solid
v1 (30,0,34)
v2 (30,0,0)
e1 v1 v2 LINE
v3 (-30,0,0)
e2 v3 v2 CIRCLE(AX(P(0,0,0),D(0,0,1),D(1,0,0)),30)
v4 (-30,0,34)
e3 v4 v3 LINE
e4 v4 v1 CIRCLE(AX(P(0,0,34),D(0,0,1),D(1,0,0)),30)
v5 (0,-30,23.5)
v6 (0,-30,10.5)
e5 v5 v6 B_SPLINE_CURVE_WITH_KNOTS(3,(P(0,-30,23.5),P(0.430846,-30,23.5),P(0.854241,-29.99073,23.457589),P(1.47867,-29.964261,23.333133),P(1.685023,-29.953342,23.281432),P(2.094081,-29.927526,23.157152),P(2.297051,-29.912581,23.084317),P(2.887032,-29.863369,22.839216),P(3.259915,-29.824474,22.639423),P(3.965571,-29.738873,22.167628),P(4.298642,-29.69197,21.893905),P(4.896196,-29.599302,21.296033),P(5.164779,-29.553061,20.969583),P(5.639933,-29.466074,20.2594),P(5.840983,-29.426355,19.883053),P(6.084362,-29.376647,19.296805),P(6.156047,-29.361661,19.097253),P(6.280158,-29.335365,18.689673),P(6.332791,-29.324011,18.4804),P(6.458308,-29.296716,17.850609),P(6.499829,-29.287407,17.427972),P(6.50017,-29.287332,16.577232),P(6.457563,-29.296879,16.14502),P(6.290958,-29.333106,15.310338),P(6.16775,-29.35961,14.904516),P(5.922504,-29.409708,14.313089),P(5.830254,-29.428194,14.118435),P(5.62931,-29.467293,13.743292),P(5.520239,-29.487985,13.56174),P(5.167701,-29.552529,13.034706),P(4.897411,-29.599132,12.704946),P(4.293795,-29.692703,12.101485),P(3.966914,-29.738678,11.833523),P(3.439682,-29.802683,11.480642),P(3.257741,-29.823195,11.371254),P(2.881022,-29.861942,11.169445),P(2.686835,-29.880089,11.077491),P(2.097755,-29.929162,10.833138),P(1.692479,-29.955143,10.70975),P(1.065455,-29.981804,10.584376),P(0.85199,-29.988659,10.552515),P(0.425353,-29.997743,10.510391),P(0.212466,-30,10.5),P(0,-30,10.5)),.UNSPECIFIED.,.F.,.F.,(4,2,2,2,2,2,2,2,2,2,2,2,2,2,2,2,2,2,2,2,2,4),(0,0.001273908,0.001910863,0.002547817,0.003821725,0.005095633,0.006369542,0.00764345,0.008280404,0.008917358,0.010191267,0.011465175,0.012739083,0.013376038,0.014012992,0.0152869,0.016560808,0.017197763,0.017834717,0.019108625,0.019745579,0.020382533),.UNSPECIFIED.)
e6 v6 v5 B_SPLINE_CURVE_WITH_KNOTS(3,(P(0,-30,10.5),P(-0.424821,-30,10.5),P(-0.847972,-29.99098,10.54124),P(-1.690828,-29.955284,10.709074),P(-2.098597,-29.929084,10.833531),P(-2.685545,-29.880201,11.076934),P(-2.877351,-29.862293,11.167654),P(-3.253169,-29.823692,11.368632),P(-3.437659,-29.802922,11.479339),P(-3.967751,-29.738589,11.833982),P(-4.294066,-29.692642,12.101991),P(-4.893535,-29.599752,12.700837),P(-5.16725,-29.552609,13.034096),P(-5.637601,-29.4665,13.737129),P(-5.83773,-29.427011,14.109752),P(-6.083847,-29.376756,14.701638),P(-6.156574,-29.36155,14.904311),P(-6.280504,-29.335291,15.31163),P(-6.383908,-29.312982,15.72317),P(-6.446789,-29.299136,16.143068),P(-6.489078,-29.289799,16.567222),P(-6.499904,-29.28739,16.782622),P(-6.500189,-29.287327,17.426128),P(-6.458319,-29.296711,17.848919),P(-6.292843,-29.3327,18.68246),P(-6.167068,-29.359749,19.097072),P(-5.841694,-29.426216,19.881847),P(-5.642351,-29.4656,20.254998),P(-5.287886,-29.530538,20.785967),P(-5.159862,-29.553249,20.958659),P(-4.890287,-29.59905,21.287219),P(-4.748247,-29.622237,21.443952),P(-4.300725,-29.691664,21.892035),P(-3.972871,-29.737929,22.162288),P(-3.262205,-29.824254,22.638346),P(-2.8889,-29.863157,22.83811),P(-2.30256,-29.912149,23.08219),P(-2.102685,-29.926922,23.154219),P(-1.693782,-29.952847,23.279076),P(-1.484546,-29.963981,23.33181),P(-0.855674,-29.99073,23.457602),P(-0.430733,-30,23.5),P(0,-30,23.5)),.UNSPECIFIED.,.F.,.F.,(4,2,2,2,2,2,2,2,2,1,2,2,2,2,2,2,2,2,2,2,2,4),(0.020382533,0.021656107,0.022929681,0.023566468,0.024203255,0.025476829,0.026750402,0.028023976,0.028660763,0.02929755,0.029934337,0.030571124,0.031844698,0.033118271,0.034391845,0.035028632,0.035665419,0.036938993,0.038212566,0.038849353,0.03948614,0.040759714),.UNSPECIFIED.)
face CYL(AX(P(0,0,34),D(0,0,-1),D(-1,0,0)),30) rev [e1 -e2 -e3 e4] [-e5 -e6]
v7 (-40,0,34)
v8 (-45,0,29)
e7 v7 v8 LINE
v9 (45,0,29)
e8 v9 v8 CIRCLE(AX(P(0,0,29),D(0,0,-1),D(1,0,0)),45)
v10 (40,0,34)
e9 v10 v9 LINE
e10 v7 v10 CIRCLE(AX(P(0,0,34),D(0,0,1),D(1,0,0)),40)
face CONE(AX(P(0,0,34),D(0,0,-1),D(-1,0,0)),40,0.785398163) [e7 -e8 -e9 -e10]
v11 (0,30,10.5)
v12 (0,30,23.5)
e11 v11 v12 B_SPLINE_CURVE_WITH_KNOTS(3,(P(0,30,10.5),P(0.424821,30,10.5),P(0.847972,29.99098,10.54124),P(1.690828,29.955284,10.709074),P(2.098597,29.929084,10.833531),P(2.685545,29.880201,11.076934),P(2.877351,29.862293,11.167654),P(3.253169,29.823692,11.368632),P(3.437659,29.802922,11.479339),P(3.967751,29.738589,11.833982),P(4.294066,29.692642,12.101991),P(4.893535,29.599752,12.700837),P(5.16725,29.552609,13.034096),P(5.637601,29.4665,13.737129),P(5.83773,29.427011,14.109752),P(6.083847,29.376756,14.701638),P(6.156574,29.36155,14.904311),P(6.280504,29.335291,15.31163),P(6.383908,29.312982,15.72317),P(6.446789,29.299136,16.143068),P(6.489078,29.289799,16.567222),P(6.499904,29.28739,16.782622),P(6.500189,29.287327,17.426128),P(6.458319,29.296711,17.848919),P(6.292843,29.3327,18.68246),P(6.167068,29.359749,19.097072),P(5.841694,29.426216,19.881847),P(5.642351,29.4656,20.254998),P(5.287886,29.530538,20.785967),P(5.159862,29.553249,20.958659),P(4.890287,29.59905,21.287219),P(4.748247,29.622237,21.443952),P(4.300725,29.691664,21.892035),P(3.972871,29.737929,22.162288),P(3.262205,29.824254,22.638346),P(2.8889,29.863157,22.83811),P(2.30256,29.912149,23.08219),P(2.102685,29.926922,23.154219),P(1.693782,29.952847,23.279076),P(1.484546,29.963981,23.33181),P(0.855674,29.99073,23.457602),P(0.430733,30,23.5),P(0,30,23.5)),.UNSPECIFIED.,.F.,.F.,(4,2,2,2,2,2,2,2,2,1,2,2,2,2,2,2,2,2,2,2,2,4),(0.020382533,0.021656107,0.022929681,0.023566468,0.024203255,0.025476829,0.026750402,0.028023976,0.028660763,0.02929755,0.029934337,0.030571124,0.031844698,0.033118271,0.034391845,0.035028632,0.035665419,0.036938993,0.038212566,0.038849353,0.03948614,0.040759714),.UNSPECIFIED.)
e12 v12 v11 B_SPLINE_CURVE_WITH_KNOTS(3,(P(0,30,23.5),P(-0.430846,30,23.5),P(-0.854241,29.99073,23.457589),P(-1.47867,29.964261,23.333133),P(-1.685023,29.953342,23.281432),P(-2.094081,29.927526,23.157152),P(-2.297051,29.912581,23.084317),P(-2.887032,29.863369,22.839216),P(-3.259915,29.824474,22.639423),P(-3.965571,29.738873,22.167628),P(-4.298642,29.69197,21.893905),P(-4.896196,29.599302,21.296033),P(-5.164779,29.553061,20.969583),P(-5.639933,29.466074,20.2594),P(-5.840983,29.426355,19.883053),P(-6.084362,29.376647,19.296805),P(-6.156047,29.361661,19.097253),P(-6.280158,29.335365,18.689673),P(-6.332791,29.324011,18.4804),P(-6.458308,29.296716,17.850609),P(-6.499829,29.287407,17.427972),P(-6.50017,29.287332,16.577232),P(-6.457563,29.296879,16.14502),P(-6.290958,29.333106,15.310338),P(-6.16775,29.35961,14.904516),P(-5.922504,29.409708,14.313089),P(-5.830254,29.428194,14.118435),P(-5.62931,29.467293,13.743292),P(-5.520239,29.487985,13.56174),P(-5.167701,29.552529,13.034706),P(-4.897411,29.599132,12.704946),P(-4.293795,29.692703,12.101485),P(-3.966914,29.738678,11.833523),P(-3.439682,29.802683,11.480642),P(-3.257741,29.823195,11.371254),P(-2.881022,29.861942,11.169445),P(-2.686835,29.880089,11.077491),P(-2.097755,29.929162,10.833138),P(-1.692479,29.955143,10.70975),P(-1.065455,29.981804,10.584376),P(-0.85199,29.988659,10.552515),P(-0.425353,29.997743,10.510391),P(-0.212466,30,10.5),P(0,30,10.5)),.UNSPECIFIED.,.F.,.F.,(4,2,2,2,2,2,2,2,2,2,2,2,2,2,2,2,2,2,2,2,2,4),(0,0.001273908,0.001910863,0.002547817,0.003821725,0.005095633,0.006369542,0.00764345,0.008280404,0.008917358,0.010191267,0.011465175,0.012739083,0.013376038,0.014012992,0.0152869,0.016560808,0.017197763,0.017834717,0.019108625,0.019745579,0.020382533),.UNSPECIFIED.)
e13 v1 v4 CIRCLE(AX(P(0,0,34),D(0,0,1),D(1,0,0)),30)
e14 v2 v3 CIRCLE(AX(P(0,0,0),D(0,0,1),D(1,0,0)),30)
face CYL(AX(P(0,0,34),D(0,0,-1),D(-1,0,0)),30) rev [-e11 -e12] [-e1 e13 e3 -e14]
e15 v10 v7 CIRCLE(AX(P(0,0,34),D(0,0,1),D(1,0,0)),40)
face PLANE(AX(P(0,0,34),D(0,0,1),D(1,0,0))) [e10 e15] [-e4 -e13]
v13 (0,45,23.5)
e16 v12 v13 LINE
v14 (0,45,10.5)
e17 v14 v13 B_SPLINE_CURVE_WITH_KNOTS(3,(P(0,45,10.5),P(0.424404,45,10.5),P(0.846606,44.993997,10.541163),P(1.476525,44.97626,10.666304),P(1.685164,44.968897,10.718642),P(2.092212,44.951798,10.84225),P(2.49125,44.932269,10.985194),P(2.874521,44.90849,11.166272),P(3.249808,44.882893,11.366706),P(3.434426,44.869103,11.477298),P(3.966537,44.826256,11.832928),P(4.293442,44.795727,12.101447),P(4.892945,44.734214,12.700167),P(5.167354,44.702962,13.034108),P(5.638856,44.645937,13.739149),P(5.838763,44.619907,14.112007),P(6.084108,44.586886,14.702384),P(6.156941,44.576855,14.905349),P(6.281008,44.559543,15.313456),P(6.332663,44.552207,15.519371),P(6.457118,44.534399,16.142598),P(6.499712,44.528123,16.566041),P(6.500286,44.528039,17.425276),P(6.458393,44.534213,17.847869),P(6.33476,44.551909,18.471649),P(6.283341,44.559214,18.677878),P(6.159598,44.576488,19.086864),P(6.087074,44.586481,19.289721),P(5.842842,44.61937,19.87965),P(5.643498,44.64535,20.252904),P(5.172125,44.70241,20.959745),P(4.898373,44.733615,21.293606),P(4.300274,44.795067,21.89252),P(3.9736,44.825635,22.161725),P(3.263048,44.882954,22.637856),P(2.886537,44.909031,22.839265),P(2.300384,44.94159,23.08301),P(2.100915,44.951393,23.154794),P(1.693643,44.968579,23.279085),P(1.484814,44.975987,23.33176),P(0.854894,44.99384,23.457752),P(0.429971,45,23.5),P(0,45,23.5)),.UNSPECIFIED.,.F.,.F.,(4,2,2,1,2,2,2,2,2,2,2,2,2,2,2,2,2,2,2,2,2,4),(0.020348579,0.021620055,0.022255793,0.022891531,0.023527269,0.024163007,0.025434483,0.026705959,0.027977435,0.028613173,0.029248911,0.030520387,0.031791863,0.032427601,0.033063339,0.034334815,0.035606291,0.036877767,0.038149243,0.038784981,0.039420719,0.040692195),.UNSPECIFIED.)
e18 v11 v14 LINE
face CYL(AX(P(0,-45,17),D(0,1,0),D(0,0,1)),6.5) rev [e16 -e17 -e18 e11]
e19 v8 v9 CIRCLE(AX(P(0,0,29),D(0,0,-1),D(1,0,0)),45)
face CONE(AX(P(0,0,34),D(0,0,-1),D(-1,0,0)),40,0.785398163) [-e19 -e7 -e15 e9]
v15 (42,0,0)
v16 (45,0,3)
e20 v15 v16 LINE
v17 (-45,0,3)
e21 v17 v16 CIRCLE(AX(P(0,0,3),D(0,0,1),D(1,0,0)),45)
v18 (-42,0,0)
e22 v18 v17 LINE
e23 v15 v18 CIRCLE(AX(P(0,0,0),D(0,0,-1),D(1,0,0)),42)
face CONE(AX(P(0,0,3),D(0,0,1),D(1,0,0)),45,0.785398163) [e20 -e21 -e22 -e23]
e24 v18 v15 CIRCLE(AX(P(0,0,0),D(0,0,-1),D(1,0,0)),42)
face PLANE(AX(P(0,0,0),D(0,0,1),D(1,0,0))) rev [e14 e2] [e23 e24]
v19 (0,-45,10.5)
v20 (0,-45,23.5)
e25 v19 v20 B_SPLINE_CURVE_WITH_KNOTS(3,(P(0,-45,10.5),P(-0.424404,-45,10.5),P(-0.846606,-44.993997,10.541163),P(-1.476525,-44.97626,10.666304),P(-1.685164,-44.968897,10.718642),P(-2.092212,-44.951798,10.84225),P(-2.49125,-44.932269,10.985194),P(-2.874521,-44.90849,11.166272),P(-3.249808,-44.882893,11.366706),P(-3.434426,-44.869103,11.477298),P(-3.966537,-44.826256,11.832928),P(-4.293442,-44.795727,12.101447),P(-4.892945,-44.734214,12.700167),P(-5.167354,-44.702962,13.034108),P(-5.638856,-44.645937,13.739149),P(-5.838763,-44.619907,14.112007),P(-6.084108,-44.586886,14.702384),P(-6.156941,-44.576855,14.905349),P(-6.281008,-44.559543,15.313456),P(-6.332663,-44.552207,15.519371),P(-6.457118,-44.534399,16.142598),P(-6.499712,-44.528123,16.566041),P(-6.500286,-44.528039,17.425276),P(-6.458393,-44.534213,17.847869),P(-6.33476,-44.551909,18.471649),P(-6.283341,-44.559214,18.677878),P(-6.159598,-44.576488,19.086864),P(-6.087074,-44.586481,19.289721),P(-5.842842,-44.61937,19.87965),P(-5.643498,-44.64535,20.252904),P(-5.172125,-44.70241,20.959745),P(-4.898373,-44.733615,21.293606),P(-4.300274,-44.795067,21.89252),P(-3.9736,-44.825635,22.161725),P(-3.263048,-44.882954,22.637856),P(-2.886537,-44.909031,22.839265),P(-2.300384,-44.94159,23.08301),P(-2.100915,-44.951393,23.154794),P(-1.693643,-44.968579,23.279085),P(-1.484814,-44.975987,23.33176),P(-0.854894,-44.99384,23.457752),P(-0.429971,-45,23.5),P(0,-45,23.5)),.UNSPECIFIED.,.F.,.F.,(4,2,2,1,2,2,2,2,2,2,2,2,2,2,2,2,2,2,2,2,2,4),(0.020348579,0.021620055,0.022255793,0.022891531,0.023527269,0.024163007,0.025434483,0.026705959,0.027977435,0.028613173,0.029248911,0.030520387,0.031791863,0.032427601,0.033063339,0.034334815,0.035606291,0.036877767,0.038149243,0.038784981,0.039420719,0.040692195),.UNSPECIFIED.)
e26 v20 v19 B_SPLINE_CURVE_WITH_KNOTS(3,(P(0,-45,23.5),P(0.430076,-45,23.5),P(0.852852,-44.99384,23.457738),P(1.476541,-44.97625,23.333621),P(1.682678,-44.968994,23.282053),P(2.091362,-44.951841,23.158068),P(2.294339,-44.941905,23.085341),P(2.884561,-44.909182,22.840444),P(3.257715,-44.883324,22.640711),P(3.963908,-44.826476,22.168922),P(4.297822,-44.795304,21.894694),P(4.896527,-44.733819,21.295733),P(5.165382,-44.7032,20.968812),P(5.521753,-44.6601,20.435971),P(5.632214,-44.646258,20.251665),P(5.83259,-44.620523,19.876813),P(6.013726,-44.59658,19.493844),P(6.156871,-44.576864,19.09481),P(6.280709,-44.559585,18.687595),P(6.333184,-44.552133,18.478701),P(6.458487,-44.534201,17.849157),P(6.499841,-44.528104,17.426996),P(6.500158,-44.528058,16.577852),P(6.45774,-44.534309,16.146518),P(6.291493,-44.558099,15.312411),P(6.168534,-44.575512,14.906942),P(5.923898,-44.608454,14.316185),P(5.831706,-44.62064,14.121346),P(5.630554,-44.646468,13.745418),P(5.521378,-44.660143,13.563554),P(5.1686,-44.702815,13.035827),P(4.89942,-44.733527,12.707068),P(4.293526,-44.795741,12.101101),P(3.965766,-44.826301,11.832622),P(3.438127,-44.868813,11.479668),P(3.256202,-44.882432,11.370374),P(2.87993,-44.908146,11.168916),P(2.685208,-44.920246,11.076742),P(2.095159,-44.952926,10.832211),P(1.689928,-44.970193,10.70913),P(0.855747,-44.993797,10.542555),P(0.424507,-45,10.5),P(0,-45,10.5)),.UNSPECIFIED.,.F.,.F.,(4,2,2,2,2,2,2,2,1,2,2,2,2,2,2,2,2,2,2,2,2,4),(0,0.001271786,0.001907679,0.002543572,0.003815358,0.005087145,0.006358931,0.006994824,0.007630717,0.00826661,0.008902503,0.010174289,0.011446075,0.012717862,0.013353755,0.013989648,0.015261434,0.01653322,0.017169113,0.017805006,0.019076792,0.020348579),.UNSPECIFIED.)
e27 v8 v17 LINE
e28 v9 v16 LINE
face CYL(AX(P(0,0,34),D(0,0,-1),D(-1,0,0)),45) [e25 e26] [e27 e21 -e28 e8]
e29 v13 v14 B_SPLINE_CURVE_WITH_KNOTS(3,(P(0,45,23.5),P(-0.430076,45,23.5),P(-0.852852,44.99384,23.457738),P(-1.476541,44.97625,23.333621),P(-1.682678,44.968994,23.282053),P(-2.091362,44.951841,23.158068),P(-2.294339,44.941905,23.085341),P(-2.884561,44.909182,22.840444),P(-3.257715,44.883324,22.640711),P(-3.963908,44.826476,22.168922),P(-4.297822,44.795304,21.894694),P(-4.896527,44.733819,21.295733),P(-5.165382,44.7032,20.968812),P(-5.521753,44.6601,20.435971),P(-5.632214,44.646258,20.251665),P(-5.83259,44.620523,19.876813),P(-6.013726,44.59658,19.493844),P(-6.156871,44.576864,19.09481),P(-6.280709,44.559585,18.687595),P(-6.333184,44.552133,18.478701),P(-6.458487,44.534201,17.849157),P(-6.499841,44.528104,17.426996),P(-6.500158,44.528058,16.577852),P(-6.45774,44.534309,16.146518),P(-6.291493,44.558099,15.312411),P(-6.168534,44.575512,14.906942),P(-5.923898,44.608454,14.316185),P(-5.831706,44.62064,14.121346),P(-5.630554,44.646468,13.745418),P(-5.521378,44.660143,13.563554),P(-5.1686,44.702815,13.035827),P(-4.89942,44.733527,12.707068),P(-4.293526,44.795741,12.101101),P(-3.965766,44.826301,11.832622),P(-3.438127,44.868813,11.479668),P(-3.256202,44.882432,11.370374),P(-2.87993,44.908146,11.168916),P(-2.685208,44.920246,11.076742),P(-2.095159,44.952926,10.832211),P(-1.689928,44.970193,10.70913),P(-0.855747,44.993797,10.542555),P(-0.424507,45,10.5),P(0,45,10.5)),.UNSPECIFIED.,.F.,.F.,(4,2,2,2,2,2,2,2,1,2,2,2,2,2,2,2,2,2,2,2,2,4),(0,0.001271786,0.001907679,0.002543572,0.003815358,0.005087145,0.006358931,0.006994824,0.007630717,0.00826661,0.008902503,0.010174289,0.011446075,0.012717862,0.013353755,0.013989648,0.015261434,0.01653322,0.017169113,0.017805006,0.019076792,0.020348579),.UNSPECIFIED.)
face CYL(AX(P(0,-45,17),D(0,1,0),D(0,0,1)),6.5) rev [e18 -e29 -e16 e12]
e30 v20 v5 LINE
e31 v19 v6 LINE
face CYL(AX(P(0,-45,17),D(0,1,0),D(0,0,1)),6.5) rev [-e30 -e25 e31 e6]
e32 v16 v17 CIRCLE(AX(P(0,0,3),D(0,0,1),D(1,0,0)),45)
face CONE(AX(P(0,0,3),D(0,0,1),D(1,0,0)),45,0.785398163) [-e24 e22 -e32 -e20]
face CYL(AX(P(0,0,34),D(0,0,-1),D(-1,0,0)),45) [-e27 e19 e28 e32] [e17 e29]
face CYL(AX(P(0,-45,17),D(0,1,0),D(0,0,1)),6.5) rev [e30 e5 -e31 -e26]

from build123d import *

# Parameters (mm, degrees)
SKETCH1_R               = 45
SKETCH1_R_2             = 30
BOSS_EXTRUDE1_DEPTH     = 34
CUT_EXTRUDE1_DEPTH      = 73.15261603
CUT_EXTRUDE1_DEPTH_BACK = 73.15261603
SKETCH3_R               = 6.5
CHAMFER1_SIZE           = 5
CHAMFER2_SIZE           = 3


with BuildPart() as part:
    # Sketch1 → Boss-Extrude1 (new body)
    with BuildSketch(Plane.XY):
        Circle(SKETCH1_R)
        Circle(SKETCH1_R_2, mode=Mode.SUBTRACT)
    extrude(amount=BOSS_EXTRUDE1_DEPTH)

    # Sketch3 → Cut-Extrude1 (cut, two sides: drawn at the far end of the back side and taken through both)
    with BuildSketch(Plane(origin=(0, 0, 0), x_dir=(1, 0, 0), z_dir=(0, 1, 0)).offset(-CUT_EXTRUDE1_DEPTH_BACK)):
        with Locations(Location((0, -17, 0), (0, 0, 270))):
            Circle(SKETCH3_R)
    extrude(amount=CUT_EXTRUDE1_DEPTH + CUT_EXTRUDE1_DEPTH_BACK, mode=Mode.SUBTRACT)

    # Chamfer1
    chamfer1_edges = [part.edges().sort_by_distance(p)[0] for p in [
        (-45, 0, 34),
    ]]
    chamfer(chamfer1_edges, length=CHAMFER1_SIZE)

    # Chamfer2
    chamfer2_edges = [part.edges().sort_by_distance(p)[0] for p in [
        (-45, 0, 0),
    ]]
    chamfer(chamfer2_edges, length=CHAMFER2_SIZE)


solid = part.part
